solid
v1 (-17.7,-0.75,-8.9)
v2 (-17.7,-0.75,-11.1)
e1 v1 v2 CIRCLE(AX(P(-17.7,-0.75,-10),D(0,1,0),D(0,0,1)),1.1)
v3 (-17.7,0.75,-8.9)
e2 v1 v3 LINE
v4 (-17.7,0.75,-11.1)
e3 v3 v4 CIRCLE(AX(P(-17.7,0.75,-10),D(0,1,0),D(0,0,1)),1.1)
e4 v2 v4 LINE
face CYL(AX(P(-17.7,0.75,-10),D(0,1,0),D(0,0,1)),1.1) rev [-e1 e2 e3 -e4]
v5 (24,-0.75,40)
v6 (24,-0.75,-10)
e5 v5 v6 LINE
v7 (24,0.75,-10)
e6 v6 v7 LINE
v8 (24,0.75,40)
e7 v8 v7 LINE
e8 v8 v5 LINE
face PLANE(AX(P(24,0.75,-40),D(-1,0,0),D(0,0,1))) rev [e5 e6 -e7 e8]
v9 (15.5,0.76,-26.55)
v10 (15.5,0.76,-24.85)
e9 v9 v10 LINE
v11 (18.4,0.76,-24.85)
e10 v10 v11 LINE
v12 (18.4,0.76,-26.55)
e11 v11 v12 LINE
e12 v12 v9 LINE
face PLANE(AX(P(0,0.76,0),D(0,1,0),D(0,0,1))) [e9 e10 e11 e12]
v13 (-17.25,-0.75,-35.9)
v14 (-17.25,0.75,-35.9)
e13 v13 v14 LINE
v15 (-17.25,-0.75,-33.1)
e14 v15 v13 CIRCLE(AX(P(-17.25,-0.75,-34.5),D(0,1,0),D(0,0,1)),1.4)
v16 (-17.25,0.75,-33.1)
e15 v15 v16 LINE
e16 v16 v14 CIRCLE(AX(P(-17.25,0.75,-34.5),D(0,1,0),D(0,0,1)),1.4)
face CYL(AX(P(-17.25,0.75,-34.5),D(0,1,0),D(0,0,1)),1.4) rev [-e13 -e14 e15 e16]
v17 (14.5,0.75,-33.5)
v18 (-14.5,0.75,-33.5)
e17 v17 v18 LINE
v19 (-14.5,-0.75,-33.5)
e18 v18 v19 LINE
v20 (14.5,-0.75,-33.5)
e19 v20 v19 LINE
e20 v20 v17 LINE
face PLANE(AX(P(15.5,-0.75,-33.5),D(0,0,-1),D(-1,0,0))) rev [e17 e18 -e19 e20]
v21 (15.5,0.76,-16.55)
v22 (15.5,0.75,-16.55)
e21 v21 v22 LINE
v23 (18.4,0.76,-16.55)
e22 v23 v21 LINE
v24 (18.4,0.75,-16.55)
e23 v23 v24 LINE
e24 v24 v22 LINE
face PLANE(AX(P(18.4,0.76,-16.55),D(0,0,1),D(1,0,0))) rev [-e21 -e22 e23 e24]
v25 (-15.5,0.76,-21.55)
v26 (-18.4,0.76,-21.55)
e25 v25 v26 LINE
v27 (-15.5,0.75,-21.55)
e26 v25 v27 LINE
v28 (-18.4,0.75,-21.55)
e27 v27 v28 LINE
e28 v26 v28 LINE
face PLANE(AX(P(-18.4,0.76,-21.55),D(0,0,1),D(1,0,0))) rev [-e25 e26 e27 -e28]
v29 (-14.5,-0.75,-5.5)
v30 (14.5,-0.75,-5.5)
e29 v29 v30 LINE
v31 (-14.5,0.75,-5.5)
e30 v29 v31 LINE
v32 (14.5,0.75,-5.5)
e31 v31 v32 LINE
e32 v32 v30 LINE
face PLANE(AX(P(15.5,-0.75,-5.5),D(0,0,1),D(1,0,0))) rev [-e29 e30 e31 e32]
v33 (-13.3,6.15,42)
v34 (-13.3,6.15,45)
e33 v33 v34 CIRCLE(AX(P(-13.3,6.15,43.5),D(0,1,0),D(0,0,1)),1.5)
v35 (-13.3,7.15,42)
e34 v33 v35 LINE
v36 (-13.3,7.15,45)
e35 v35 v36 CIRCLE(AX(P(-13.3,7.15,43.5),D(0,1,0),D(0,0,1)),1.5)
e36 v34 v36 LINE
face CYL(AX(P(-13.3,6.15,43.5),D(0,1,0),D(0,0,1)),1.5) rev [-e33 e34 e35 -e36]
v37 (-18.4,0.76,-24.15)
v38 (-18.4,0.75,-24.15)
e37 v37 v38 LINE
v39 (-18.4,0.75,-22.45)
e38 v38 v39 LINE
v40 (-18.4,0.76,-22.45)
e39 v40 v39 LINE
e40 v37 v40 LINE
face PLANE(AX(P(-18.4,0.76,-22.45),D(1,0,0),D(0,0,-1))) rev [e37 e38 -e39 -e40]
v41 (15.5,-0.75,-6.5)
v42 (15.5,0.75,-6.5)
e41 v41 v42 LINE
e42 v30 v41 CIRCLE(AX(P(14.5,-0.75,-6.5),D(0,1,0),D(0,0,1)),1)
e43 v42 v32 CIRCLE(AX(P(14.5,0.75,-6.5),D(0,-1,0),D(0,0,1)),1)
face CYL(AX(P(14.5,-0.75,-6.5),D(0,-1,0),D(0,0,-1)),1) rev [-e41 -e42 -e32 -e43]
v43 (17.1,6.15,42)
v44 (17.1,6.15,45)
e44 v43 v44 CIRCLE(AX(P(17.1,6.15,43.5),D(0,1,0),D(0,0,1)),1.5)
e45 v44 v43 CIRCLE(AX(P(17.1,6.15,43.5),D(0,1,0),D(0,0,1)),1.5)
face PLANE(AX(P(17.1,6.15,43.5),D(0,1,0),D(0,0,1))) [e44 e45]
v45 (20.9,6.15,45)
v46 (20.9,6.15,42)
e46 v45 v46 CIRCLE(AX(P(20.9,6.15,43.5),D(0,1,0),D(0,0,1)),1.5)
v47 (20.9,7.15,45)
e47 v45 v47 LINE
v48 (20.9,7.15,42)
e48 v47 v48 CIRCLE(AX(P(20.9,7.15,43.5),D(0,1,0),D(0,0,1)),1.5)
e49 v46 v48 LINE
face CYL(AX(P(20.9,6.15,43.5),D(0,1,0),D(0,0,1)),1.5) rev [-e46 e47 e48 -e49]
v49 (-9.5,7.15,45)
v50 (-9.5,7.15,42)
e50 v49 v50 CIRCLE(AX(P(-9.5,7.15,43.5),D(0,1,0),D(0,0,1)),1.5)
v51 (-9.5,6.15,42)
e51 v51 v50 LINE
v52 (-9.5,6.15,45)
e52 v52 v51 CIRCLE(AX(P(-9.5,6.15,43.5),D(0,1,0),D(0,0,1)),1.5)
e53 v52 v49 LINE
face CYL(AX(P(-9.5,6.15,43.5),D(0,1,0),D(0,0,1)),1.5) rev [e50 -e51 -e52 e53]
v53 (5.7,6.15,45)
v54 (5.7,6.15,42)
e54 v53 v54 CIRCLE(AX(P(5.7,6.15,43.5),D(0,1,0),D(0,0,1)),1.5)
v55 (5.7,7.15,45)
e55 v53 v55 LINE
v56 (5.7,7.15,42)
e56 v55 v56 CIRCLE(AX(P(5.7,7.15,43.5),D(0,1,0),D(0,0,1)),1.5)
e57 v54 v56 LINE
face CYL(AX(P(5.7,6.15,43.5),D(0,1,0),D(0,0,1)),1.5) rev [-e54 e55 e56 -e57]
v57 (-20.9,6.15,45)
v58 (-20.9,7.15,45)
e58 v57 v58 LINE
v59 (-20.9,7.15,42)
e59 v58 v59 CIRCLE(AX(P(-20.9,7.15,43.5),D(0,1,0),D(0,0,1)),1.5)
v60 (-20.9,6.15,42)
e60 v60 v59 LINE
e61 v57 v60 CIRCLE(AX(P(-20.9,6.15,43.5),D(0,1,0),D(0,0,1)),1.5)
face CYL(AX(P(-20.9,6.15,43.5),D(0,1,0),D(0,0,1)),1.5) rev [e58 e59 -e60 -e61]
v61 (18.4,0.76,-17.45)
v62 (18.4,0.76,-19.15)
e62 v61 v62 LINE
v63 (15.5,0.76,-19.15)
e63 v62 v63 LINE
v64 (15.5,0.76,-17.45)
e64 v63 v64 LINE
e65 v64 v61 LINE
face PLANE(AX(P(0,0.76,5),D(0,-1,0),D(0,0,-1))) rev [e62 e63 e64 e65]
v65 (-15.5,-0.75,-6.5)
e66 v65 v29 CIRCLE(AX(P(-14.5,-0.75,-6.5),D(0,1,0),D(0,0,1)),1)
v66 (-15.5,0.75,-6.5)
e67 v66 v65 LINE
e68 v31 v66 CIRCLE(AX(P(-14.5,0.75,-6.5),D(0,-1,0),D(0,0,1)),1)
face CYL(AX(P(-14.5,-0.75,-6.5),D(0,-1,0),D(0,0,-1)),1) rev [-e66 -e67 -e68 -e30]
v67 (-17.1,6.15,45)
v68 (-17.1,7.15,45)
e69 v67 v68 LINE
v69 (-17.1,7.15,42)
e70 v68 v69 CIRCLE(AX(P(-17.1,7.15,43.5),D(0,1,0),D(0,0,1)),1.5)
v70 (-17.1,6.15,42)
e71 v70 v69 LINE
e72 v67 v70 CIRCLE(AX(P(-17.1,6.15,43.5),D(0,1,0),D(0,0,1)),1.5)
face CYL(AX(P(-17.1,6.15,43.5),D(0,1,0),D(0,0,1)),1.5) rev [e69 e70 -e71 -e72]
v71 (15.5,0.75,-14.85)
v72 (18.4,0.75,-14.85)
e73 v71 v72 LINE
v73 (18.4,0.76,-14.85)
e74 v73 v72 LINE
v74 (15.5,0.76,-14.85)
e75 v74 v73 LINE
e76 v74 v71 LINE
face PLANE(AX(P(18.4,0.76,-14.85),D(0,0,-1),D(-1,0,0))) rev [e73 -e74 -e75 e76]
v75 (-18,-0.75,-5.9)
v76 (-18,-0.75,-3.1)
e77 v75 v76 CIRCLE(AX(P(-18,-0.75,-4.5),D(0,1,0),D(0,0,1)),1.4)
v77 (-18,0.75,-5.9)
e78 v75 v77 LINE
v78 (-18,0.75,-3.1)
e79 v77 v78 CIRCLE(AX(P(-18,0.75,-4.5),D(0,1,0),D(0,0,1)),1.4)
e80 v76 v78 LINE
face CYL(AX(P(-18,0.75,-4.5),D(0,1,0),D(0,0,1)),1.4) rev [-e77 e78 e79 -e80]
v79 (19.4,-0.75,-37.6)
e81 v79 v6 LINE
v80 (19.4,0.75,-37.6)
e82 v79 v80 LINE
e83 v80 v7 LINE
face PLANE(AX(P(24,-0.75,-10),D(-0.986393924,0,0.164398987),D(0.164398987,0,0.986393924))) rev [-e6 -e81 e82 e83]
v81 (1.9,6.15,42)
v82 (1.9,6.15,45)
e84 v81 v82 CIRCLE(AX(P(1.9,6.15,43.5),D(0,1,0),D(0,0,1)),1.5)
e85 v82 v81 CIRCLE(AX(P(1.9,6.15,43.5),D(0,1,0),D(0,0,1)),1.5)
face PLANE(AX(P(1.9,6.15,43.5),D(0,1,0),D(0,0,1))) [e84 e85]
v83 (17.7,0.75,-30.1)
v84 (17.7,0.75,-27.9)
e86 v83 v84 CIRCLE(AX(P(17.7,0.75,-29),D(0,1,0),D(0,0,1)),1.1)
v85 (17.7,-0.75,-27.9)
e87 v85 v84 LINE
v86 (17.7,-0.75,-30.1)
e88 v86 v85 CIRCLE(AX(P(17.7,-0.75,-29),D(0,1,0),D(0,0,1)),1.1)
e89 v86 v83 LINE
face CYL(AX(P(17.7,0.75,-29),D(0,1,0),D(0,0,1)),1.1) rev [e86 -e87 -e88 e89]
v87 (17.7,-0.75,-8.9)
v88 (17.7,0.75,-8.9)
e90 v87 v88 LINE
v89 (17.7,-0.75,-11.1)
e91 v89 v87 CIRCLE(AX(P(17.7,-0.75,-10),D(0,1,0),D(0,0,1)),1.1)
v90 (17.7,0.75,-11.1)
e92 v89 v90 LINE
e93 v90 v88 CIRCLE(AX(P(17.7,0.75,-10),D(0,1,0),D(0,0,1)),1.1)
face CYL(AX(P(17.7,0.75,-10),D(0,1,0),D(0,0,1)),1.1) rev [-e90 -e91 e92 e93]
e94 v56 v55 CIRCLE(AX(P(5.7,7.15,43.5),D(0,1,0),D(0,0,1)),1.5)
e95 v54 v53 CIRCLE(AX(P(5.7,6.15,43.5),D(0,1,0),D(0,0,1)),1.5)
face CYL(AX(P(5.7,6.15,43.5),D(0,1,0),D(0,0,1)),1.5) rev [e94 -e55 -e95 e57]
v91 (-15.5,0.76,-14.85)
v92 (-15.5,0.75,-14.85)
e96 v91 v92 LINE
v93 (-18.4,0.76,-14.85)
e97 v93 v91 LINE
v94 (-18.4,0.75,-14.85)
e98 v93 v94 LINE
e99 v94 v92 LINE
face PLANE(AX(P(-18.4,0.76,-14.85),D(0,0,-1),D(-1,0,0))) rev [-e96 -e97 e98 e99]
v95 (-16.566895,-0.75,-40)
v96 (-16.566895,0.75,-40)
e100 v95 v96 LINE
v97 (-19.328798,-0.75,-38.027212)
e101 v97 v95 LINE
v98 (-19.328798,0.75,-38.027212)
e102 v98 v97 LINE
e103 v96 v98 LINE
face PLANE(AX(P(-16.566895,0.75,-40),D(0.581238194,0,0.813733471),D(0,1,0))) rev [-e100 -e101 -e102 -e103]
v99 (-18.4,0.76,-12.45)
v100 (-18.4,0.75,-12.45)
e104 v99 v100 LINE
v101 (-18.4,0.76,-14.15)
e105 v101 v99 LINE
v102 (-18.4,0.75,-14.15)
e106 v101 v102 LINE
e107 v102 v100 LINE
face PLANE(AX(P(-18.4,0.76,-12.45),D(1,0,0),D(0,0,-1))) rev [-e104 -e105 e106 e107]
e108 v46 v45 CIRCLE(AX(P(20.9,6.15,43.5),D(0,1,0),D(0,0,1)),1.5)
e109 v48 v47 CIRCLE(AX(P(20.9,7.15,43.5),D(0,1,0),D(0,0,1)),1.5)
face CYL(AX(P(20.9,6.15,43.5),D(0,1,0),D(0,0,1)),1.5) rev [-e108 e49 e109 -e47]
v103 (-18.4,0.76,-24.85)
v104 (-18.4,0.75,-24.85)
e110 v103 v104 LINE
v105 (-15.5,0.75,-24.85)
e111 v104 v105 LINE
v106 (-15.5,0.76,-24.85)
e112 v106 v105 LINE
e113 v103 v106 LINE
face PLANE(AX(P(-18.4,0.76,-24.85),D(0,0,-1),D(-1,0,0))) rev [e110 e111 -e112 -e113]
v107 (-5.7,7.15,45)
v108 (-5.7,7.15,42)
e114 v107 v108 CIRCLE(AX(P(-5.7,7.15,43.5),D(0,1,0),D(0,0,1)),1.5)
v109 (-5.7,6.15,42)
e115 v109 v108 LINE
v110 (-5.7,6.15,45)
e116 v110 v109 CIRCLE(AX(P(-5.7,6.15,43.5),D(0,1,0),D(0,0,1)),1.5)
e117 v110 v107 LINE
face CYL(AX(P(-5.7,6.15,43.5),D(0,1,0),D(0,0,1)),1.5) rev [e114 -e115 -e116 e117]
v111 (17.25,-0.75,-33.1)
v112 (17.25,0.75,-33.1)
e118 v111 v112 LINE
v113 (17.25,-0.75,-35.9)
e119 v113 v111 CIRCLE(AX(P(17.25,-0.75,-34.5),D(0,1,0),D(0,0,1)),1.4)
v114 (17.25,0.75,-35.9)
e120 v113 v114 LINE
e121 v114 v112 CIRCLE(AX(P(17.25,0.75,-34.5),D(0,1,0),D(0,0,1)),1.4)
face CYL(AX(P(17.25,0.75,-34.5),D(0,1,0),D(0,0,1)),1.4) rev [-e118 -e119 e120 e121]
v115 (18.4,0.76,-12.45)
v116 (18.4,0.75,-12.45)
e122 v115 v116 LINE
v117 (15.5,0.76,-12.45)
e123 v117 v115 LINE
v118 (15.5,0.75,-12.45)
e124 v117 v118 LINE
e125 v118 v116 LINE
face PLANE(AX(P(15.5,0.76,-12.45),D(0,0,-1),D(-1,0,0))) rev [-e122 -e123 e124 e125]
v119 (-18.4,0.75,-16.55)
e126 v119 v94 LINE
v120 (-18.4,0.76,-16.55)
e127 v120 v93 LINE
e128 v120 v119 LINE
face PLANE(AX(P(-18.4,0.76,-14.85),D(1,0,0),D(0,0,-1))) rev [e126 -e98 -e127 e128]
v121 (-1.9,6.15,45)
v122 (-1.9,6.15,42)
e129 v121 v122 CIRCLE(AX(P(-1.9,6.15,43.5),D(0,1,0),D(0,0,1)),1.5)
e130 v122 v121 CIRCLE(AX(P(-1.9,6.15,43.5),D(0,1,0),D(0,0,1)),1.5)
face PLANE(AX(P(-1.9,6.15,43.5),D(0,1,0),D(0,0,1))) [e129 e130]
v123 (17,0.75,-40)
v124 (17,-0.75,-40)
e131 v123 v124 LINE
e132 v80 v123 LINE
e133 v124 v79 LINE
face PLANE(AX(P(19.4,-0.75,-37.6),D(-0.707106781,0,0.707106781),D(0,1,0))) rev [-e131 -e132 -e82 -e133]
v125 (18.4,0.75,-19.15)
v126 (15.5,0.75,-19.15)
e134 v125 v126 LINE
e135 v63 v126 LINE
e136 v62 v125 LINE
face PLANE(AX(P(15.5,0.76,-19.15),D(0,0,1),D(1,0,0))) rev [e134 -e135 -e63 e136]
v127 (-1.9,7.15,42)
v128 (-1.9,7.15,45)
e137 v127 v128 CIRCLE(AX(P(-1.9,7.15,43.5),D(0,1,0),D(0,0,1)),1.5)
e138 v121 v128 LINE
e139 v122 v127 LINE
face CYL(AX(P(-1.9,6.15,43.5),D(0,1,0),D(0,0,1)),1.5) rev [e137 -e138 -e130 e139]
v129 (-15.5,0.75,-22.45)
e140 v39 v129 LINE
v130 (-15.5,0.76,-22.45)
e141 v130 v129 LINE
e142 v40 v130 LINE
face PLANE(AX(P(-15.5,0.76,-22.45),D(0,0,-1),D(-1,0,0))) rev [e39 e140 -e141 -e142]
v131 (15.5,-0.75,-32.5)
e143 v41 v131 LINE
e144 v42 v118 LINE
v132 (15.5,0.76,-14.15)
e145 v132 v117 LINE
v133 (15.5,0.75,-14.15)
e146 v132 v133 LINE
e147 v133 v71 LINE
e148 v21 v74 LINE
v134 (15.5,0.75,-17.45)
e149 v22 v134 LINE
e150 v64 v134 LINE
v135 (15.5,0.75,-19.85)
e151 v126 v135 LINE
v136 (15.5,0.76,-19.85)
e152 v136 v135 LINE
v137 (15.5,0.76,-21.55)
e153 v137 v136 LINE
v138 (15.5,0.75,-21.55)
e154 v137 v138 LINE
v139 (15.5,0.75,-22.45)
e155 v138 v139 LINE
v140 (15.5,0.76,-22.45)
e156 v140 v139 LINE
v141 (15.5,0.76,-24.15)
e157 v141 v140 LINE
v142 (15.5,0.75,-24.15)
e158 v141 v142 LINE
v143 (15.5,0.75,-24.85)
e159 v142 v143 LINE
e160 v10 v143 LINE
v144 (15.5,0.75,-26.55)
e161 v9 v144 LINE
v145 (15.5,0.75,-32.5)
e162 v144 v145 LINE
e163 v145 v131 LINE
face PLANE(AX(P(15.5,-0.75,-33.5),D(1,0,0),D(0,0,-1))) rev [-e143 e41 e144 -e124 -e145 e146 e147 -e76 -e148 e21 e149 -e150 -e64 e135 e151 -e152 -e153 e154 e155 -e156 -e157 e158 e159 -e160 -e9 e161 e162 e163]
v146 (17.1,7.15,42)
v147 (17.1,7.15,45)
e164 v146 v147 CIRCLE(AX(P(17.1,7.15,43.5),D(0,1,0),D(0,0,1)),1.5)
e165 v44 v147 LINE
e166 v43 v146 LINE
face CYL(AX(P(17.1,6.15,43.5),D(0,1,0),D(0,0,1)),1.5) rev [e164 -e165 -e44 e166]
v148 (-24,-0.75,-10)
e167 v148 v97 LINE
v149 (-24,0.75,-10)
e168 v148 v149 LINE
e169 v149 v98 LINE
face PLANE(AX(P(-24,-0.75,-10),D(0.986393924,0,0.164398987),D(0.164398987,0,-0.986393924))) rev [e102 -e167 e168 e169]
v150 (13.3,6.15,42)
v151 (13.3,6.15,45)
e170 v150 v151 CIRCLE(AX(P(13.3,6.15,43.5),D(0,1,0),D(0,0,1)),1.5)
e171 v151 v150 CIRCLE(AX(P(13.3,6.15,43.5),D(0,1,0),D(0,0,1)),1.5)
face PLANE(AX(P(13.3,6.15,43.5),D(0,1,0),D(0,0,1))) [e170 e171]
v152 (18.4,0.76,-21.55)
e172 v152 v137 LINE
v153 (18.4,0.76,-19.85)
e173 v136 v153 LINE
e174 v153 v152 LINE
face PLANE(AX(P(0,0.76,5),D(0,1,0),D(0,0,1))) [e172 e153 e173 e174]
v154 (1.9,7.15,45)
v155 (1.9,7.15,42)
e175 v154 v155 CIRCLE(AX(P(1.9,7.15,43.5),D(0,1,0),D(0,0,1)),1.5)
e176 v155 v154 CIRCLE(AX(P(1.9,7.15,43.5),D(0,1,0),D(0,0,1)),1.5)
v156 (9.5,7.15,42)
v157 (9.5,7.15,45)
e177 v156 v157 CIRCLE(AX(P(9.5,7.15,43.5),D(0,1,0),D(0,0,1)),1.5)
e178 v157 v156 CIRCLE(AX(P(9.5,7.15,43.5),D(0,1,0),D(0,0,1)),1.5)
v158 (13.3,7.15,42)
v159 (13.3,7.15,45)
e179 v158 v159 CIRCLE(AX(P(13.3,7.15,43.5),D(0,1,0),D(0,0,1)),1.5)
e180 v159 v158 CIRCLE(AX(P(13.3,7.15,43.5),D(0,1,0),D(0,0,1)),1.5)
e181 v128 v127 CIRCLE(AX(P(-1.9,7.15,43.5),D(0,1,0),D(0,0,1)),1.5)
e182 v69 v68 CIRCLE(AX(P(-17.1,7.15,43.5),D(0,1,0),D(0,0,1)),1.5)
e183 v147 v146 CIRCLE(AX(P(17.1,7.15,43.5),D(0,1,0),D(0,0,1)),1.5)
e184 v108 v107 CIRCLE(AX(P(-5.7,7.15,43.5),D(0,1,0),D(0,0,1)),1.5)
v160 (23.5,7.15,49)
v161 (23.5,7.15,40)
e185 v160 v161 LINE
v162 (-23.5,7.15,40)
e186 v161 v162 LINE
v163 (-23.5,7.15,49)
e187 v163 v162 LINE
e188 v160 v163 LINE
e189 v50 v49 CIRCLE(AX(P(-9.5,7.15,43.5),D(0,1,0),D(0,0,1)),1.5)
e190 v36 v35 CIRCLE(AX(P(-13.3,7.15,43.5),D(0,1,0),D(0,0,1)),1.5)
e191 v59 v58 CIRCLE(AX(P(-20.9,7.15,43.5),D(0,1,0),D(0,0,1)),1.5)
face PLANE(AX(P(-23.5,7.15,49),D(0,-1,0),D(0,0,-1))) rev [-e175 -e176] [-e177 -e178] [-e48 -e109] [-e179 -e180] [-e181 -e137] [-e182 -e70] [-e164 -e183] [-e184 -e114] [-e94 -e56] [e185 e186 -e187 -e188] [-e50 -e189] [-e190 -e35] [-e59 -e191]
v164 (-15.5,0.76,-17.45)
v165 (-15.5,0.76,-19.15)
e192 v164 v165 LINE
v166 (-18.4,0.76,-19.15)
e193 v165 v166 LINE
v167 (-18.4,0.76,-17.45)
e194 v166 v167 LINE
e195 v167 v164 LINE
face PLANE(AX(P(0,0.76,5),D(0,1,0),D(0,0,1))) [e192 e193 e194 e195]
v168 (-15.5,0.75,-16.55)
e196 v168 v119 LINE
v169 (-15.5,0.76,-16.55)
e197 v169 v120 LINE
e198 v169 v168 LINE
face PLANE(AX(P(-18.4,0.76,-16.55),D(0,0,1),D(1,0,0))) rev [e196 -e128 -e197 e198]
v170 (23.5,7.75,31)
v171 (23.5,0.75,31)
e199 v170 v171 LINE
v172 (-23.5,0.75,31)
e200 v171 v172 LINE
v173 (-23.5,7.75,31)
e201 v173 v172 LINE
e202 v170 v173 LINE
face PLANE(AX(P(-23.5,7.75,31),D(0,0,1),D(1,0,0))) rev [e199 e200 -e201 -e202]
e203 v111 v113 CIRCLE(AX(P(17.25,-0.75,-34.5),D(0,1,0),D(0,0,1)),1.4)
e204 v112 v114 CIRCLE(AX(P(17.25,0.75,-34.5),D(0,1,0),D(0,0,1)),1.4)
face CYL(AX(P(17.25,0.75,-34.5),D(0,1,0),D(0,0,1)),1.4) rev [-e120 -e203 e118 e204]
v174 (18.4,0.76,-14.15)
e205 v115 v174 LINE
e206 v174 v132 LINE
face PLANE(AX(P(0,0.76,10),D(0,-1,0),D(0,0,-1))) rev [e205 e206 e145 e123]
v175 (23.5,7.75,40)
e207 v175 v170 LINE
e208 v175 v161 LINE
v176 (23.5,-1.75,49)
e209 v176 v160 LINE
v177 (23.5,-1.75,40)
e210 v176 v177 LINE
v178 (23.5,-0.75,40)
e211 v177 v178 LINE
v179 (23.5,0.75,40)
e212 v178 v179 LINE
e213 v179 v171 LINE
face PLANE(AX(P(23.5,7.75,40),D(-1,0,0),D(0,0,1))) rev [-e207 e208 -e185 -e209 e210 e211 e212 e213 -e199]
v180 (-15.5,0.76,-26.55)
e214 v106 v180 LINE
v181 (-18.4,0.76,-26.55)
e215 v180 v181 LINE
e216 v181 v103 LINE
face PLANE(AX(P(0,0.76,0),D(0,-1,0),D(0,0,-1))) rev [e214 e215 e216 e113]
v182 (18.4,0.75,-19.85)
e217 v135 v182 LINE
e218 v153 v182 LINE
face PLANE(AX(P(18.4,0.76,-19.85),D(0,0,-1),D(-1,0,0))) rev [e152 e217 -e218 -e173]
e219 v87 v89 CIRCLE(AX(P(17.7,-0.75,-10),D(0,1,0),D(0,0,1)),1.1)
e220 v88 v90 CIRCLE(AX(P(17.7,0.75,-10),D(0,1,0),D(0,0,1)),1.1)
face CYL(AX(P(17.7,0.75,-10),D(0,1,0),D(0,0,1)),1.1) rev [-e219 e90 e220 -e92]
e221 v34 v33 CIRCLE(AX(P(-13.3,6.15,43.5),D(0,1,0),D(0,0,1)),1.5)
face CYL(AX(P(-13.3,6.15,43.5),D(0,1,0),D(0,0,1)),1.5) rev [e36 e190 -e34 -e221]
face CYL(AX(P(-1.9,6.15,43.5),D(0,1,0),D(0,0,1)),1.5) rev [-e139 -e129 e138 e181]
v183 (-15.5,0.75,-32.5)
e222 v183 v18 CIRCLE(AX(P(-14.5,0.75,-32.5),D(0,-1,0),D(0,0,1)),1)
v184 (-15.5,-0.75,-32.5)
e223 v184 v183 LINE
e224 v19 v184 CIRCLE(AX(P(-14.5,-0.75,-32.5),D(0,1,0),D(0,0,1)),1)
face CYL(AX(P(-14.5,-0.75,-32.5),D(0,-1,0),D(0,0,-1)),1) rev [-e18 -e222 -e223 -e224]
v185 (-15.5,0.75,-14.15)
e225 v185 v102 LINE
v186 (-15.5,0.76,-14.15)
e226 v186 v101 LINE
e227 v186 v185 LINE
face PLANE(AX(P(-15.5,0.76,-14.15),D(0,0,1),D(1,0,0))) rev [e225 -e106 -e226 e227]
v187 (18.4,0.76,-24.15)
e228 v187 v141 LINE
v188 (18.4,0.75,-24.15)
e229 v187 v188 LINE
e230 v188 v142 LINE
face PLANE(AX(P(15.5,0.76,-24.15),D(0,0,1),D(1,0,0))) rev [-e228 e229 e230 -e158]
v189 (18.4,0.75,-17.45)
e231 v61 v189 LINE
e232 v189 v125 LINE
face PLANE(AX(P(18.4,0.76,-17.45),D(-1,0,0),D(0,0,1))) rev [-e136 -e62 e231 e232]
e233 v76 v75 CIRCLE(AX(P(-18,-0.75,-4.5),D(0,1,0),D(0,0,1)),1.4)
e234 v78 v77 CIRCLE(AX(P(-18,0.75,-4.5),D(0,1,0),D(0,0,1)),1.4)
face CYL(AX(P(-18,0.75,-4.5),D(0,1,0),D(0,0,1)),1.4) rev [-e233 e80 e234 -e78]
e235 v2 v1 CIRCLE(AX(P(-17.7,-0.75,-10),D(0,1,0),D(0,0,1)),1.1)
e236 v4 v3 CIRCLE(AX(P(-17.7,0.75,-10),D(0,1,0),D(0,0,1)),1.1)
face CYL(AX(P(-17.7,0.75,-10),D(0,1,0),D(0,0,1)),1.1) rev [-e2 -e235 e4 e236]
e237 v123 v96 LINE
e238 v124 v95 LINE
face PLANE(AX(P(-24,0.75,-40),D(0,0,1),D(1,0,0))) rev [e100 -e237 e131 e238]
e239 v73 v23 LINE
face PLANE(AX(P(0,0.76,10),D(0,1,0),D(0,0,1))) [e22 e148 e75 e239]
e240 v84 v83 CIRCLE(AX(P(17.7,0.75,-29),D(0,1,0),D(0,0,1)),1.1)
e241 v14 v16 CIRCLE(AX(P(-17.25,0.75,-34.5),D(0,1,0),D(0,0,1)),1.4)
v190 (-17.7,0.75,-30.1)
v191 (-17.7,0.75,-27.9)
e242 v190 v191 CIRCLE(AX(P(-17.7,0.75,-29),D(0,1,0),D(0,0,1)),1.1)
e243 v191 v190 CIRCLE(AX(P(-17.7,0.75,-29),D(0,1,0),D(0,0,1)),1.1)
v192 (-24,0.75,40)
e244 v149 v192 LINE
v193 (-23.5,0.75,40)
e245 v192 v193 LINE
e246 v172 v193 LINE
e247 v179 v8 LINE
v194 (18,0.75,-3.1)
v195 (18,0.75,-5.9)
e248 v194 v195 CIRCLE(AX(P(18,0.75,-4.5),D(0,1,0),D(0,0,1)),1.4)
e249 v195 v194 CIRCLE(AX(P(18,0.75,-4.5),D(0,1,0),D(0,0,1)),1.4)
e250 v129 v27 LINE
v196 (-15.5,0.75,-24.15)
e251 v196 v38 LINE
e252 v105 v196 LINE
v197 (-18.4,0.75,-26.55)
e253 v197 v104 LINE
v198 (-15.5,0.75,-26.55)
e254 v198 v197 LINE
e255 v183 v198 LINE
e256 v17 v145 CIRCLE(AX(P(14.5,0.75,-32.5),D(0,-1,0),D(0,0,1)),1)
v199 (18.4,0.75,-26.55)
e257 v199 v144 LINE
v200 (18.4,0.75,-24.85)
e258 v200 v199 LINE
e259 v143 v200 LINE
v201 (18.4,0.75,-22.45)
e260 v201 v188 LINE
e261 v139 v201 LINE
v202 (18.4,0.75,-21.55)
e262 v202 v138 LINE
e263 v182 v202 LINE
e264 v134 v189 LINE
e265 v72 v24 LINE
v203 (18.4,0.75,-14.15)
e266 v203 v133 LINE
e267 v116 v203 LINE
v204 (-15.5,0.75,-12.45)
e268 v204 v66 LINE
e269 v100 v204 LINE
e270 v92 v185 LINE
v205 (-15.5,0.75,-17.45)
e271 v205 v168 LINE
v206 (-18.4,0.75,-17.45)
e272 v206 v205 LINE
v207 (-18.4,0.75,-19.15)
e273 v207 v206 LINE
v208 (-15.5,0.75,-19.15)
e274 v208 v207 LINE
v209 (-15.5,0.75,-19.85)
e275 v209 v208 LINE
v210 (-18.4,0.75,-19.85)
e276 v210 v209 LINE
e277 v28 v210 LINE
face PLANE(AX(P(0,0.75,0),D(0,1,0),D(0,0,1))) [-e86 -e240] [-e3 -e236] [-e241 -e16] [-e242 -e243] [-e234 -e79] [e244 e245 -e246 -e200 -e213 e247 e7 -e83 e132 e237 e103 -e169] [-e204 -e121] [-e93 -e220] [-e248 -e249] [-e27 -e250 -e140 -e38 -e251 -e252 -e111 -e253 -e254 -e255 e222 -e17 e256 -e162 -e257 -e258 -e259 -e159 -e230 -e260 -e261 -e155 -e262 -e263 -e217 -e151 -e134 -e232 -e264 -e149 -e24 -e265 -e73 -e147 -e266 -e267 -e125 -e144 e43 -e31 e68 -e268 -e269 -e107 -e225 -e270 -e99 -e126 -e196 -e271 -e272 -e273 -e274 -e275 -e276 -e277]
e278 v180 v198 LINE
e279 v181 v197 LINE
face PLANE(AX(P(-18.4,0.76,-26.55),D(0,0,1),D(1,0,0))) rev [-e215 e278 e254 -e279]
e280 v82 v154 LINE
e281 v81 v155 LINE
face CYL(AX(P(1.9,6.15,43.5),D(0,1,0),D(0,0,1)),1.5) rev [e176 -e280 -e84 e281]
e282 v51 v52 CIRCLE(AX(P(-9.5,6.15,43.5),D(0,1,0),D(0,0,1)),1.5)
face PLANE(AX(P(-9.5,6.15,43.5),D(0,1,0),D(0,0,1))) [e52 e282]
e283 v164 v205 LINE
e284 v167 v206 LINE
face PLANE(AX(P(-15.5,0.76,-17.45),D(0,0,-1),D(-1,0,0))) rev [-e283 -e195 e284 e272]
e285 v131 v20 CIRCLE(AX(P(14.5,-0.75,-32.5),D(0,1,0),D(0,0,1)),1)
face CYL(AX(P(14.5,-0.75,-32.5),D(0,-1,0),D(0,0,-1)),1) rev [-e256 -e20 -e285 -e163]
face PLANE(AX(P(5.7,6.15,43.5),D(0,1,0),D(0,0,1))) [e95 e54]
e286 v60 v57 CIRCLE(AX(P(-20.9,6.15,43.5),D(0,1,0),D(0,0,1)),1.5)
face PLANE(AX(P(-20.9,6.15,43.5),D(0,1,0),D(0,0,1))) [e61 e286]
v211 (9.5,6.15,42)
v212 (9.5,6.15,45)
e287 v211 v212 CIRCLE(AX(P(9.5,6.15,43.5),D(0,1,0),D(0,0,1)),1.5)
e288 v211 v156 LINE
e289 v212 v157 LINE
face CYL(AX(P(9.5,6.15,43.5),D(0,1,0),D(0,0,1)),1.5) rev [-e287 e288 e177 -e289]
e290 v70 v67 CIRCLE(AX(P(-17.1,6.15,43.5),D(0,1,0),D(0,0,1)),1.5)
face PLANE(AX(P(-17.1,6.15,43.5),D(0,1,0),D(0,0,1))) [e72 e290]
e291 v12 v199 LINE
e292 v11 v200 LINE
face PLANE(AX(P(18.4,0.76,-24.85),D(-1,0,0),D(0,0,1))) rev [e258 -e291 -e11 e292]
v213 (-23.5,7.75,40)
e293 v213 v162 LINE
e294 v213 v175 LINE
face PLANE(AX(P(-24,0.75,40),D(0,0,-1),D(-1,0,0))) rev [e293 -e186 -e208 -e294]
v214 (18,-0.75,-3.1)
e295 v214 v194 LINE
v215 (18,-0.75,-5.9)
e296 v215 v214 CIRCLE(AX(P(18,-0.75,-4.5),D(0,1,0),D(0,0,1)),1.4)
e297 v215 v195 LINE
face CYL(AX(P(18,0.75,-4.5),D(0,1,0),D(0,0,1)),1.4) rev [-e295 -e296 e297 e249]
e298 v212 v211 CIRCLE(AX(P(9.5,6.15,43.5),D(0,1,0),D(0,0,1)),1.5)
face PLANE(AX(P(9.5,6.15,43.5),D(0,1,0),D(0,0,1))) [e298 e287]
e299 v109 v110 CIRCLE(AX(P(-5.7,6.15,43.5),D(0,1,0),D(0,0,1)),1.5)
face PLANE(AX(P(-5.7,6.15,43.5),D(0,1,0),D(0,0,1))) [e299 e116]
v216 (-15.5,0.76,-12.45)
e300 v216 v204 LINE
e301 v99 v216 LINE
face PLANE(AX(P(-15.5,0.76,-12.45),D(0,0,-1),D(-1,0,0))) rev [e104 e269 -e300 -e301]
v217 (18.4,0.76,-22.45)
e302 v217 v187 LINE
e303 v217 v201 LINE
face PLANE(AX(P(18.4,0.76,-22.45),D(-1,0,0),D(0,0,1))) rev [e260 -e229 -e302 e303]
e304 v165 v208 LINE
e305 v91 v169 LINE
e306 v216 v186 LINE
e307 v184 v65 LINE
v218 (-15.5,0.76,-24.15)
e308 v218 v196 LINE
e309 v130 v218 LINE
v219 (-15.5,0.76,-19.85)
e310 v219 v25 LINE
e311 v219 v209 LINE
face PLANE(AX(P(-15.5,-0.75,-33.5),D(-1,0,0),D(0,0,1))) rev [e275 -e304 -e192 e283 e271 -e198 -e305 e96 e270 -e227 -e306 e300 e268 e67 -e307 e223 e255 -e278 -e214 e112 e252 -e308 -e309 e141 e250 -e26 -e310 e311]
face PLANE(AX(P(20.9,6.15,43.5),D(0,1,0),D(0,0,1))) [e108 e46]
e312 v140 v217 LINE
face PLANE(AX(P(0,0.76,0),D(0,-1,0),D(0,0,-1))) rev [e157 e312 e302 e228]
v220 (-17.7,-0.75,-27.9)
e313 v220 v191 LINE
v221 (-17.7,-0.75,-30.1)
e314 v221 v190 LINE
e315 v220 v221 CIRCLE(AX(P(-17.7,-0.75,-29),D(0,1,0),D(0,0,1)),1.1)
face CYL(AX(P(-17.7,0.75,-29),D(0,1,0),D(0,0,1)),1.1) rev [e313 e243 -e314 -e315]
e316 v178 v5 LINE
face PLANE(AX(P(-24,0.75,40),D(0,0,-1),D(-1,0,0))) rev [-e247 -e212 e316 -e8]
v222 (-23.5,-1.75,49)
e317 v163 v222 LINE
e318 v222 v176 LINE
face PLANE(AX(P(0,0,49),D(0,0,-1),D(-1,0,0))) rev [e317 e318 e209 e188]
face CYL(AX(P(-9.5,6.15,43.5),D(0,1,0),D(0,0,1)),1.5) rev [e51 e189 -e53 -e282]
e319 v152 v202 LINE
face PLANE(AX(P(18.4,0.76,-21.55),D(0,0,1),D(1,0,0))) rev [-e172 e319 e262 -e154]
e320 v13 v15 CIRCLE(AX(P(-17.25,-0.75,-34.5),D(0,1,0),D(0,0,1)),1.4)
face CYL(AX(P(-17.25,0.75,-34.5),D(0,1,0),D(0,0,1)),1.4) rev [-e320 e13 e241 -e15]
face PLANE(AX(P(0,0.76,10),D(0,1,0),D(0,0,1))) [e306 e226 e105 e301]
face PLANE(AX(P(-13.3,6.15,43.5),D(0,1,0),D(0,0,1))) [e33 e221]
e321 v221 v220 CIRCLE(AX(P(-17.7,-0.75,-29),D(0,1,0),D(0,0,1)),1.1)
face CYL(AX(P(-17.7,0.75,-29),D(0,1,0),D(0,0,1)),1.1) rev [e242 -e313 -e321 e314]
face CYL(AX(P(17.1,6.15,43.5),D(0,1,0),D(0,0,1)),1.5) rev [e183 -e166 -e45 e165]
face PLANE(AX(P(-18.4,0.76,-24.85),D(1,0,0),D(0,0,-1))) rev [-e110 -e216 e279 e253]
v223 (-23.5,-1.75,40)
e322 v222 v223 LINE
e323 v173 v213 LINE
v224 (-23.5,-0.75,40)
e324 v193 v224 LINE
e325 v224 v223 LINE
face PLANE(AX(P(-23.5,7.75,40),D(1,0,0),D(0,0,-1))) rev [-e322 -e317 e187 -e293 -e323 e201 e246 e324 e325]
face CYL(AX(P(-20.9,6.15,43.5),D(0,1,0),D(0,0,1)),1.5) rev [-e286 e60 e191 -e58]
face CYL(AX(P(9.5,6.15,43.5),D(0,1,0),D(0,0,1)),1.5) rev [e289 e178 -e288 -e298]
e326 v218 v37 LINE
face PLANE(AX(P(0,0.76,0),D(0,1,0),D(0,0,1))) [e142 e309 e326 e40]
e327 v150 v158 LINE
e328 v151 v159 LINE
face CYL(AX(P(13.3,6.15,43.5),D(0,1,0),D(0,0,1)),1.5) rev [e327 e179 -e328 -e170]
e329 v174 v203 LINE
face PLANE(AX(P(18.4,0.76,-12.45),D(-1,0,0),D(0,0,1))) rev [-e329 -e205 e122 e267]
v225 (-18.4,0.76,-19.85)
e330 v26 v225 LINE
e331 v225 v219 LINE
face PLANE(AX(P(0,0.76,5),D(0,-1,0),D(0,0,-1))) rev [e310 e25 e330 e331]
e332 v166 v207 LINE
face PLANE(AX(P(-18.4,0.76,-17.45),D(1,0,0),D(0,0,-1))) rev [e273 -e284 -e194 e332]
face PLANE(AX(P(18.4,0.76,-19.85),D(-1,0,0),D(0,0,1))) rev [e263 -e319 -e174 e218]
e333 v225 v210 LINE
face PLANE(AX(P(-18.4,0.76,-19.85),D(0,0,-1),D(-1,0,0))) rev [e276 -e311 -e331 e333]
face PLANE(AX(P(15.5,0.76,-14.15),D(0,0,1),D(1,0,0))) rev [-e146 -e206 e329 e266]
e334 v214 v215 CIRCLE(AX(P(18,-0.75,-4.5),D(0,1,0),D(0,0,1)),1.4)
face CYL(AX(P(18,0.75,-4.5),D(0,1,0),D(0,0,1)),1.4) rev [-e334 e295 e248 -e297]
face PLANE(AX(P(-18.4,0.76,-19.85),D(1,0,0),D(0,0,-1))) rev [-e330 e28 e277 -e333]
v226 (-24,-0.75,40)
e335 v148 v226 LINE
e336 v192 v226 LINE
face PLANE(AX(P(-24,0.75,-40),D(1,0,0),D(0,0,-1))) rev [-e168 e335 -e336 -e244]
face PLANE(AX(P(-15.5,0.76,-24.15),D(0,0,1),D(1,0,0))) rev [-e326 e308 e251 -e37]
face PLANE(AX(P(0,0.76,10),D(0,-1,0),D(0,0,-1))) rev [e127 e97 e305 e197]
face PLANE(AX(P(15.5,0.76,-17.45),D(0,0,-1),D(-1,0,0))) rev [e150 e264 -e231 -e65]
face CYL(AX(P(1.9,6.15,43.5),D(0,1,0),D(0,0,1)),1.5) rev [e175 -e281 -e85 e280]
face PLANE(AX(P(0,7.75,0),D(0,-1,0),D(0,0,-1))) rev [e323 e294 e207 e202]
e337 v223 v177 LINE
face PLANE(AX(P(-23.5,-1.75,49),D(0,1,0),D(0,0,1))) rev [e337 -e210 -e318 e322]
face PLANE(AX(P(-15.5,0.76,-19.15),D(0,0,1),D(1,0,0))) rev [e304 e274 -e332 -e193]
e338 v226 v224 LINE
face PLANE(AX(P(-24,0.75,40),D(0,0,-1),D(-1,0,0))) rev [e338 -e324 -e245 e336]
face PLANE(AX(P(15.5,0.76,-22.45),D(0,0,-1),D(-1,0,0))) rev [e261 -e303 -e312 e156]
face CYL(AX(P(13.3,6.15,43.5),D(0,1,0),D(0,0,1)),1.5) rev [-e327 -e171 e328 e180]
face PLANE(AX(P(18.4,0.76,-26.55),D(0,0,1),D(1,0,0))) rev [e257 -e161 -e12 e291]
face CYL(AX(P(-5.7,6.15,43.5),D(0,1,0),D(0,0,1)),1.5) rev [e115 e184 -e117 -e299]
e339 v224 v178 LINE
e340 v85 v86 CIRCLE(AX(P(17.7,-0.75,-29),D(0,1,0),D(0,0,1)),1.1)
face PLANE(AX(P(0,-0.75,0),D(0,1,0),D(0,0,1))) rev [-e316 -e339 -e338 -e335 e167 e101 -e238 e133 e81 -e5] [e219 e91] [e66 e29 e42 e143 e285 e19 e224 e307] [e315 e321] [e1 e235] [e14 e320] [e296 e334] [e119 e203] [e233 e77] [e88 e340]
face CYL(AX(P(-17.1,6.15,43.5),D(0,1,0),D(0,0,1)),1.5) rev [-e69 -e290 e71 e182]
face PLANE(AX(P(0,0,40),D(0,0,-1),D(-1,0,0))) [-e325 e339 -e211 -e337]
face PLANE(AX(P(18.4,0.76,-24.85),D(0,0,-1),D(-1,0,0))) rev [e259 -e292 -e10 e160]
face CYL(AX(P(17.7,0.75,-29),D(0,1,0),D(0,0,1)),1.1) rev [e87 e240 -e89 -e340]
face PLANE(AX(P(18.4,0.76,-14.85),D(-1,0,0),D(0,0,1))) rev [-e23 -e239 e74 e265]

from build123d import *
from OCP.BRepFilletAPI import BRepFilletAPI_MakeChamfer

# Parameters (mm, degrees)
SKETCH1_W                  = 48
SKETCH1_H                  = 80
BOSS_EXTRUDE1_DEPTH        = 0.75
CUT_EXTRUDE1_DEPTH         = 47.671725916
SKETCH3_W                  = 31
SKETCH3_H                  = 28
CUT_EXTRUDE2_DEPTH         = 47.671725916
FILLET1_R                  = 1
F_2_8_2_8_DIAMETER_HOLE1_D = 2.8
F_2_2_2_2_DIAMETER_HOLE1_D = 2.2
SKETCH8_W                  = 47
SKETCH8_H                  = 9
BOSS_EXTRUDE2_DEPTH        = 7
SKETCH9_W                  = 47
SKETCH9_H                  = 8.9
BOSS_EXTRUDE3_DEPTH        = 9
SKETCH10_R                 = 1.5
CUT_EXTRUDE3_DEPTH         = 1
LPATTERN1_COUNT            = 12
LPATTERN1_PITCH            = 3.8
SKETCH11_W                 = 2.9
SKETCH11_H                 = 1.7
BOSS_EXTRUDE4_DEPTH        = 0.01
LPATTERN2_COUNT            = 3
LPATTERN2_PITCH            = 5
CHAMFER1_SIZE              = 2
CHAMFER1_SIZE2             = 2.433105012


with BuildPart() as part:
    # Sketch1 → Boss-Extrude1 (new, symmetric)
    with BuildSketch(Plane(origin=(0, 0, 0), x_dir=(1, 0, 0), z_dir=(0, 1, 0))):
        Rectangle(SKETCH1_W, SKETCH1_H)
    extrude(amount=BOSS_EXTRUDE1_DEPTH, both=True)

    # Sketch2 → Cut-Extrude1 (cut, through all)
    with BuildSketch(Plane(origin=(0, 0.75, 0), x_dir=(1, 0, 0), z_dir=(0, 1, 0))):
        Polygon((-19, 40), (-24, 40), (-24, 10), align=None)
        Polygon((19, 40), (24, 40), (24, 10), align=None)
    extrude(amount=-CUT_EXTRUDE1_DEPTH, mode=Mode.SUBTRACT)

    # Sketch3 → Cut-Extrude2 (cut, through all)
    with BuildSketch(Plane(origin=(0, 0.75, 0), x_dir=(1, 0, 0), z_dir=(0, 1, 0))):
        with Locations((0, 19.5)):
            Rectangle(SKETCH3_W, SKETCH3_H)
    extrude(amount=-CUT_EXTRUDE2_DEPTH, mode=Mode.SUBTRACT)

    # Fillet1
    fillet1_edges = [part.edges().sort_by_distance(p)[0] for p in [
        (15.5, 0, -33.5),
        (15.5, 0, -5.5),
        (-15.5, 0, -5.5),
        (-15.5, 0, -33.5),
    ]]
    fillet(fillet1_edges, radius=FILLET1_R)

    # Ø2.8 (2.8) Diameter Hole1 (through all)
    with Locations(Plane(origin=(0, 0.75, 0), x_dir=(1, 0, 0), z_dir=(0, 1, 0))):
        with Locations((17.25, 34.5), (18, 4.5), (-17.25, 34.5), (-18, 4.5)):
            Hole(F_2_8_2_8_DIAMETER_HOLE1_D / 2)

    # Ø2.2 (2.2) Diameter Hole1 (through all)
    with Locations(Plane(origin=(0, 0.75, 0), x_dir=(1, 0, 0), z_dir=(0, 1, 0))):
        with Locations((17.7, 29), (17.7, 10), (-17.7, 10), (-17.7, 29)):
            Hole(F_2_2_2_2_DIAMETER_HOLE1_D / 2)

    # Sketch8 → Boss-Extrude2 (add)
    with BuildSketch(Plane(origin=(0, 0.75, 0), x_dir=(1, 0, 0), z_dir=(0, 1, 0))):
        with Locations((0, -35.5)):
            Rectangle(SKETCH8_W, SKETCH8_H)
    extrude(amount=BOSS_EXTRUDE2_DEPTH)

    # Sketch9 → Boss-Extrude3 (add)
    with BuildSketch(Plane.XY.offset(40)):
        with Locations((0, 2.7)):
            Rectangle(SKETCH9_W, SKETCH9_H)
    extrude(amount=BOSS_EXTRUDE3_DEPTH)

    # Sketch10 → Cut-Extrude3 (cut)
    with BuildSketch(Plane(origin=(0, 7.15, 0), x_dir=(1, 0, 0), z_dir=(0, 1, 0))):
        with Locations(Location((-20.9, -43.5, 0), (0, 0, 270))):
            Circle(SKETCH10_R)
    cut_extrude3 = extrude(amount=-CUT_EXTRUDE3_DEPTH, mode=Mode.SUBTRACT)

    # LPattern1: Cut-Extrude3 ×12
    with Locations(*[(i * LPATTERN1_PITCH, 0, 0) for i in range(1, LPATTERN1_COUNT)]):
        add(cut_extrude3, mode=Mode.SUBTRACT)

    # Sketch11 → Boss-Extrude4 (add)
    with BuildSketch(Plane(origin=(0, 0.75, 0), x_dir=(1, 0, 0), z_dir=(0, 1, 0))):
        with Locations((-16.95, 23.3)):
            Rectangle(SKETCH11_W, SKETCH11_H)
        with Locations((16.95, 25.7)):
            Rectangle(SKETCH11_W, SKETCH11_H)
        with Locations((-16.95, 25.7)):
            Rectangle(SKETCH11_W, SKETCH11_H)
        with Locations((16.95, 23.3)):
            Rectangle(SKETCH11_W, SKETCH11_H)
    boss_extrude4 = extrude(amount=BOSS_EXTRUDE4_DEPTH)

    # LPattern2: Boss-Extrude4 ×3
    with Locations(*[(0, 0, i * LPATTERN2_PITCH) for i in range(1, LPATTERN2_COUNT)]):
        add(boss_extrude4)

    # Chamfer1: one chamfer whose edges measure the first distance from different faces: ONE call of the kernel's chamfer builder (chamfer() names one face for all edges)
    chamfer1_edges_1 = [part.edges().sort_by_distance(p)[0] for p in [
        (-19, 0, -40),
    ]]
    chamfer1_side_1 = [part.faces().sort_by_distance(p)[0] for p in [
        (-21.5, 0, -25),
    ]]
    chamfer1_edges_2 = [part.edges().sort_by_distance(p)[0] for p in [
        (19, 0, -40),
    ]]
    chamfer1_side_2 = [part.faces().sort_by_distance(p)[0] for p in [
        (0, 0, -40),
    ]]
    chamfer1 = BRepFilletAPI_MakeChamfer(part.part.solid().wrapped)
    for e in chamfer1_edges_1:
        chamfer1.Add(CHAMFER1_SIZE, CHAMFER1_SIZE2, e.wrapped, chamfer1_side_1[0].wrapped)  # the first distance lies on this face
    for e in chamfer1_edges_2:
        chamfer1.Add(CHAMFER1_SIZE, CHAMFER1_SIZE2, e.wrapped, chamfer1_side_2[0].wrapped)  # the first distance lies on this face
    add(Compound.cast(chamfer1.Shape()), mode=Mode.REPLACE)


solid = part.part
